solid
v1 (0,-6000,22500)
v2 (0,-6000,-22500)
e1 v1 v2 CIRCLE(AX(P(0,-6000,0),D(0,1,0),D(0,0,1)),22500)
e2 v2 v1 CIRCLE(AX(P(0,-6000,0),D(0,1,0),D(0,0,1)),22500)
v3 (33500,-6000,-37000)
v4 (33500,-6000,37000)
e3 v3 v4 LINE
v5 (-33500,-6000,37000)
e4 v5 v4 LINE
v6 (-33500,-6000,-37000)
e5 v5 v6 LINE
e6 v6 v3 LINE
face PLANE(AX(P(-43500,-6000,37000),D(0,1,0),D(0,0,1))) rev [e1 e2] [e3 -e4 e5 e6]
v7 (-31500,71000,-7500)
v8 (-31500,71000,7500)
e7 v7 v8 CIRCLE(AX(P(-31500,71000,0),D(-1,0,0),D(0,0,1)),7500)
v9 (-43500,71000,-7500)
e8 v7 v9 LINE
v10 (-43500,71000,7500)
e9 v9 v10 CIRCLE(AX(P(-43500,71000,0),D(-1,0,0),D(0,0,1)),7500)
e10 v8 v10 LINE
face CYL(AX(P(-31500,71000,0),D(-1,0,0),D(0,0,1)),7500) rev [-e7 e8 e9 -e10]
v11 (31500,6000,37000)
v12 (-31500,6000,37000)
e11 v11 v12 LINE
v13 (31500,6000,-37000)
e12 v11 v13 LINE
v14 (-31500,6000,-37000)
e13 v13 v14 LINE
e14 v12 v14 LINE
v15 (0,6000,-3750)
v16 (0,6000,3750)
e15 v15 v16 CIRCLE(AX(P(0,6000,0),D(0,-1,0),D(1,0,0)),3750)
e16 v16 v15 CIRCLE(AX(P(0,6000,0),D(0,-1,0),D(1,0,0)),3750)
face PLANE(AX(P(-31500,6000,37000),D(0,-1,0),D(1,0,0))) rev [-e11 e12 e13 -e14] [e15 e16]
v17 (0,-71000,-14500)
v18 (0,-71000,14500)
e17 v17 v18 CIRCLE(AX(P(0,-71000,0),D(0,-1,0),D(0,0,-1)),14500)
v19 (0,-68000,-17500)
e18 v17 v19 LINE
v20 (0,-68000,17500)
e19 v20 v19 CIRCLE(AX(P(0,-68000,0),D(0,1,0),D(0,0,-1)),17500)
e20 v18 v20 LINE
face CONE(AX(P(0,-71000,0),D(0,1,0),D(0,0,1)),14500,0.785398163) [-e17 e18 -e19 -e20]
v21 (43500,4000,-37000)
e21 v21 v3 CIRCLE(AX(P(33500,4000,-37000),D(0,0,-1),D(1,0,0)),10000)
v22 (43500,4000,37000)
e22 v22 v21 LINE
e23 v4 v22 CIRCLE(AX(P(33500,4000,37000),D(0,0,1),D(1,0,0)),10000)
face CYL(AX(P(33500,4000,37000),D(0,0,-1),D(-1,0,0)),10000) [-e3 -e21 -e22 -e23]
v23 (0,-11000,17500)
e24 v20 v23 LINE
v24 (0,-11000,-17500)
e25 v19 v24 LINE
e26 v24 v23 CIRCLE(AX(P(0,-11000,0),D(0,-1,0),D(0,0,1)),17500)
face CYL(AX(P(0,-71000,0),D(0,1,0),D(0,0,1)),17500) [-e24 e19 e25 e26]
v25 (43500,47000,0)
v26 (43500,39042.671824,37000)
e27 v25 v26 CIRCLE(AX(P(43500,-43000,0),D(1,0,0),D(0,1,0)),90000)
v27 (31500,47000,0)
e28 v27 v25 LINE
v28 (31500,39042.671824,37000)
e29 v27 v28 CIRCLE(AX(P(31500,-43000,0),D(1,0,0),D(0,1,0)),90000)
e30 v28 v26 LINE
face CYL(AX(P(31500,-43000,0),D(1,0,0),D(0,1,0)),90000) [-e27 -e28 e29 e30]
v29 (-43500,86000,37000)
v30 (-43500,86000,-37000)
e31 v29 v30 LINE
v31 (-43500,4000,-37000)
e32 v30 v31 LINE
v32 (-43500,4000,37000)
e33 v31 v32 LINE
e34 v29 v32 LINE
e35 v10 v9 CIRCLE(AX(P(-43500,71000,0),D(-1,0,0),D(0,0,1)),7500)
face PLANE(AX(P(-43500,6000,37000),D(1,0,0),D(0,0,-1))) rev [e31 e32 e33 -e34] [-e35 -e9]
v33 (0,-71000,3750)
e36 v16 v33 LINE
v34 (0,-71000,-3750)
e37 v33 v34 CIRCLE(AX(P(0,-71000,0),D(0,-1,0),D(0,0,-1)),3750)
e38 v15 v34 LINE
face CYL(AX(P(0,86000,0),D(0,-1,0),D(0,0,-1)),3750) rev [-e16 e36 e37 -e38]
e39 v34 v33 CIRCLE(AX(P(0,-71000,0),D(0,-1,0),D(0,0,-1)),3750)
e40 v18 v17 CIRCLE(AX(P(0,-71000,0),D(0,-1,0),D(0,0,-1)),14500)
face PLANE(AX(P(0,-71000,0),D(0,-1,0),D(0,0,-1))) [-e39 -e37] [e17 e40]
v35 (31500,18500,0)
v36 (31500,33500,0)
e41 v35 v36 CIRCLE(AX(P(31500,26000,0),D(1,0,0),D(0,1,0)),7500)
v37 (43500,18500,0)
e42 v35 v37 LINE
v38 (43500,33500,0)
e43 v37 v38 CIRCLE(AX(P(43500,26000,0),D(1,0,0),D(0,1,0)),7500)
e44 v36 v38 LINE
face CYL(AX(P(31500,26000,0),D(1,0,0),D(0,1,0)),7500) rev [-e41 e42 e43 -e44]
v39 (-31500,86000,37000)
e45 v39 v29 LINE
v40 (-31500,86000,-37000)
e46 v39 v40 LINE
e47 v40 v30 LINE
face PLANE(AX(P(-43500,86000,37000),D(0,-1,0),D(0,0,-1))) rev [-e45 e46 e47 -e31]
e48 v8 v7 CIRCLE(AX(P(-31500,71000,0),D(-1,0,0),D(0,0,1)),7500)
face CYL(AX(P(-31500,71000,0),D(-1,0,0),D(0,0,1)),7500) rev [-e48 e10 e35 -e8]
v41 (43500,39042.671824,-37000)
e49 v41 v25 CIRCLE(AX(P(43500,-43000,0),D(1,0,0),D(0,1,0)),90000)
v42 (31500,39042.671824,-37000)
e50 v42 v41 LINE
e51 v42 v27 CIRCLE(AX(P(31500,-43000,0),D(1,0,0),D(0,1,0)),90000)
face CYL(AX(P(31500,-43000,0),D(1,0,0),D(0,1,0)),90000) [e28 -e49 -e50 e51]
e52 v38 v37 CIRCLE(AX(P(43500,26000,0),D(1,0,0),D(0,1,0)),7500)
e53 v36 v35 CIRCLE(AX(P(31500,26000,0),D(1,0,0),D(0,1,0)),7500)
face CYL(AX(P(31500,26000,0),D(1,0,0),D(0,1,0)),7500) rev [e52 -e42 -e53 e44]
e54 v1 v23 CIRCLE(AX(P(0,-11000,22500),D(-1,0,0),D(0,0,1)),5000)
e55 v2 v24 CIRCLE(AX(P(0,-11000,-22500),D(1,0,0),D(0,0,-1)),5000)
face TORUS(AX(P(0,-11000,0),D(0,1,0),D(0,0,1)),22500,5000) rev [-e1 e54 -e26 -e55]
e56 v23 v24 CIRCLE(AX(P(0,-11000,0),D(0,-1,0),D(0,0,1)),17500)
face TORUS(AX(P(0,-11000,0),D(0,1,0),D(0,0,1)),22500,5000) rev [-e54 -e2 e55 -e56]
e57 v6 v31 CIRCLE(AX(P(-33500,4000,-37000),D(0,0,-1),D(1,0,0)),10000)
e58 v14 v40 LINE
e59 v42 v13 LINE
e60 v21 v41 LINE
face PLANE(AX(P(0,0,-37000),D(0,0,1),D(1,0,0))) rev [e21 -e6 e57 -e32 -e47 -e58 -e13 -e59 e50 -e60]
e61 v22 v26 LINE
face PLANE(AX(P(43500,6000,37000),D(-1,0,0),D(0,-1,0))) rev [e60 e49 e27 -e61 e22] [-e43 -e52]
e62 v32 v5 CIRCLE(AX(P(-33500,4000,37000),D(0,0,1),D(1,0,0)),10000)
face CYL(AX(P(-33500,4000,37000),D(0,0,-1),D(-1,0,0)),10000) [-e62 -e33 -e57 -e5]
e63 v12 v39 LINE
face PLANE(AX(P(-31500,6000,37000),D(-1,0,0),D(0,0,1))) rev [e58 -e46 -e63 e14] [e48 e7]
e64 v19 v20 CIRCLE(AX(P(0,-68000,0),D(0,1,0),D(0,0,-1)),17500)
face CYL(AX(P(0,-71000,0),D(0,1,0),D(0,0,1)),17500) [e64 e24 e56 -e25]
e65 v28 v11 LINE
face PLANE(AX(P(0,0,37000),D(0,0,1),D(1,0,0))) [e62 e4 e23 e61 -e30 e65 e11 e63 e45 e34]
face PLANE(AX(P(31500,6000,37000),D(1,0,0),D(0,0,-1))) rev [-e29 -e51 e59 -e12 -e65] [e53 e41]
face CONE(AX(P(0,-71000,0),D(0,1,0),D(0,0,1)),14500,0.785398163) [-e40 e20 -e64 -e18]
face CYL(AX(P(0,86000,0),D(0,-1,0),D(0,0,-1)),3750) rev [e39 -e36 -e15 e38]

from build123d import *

# Parameters (mm, degrees)
U_BRACKET_BODY_DEPTH                = 37000
CORNER_FILLET_R10_A_R               = 10000
CORNER_FILLET_R10_B_R               = 10000
SHORT_ARM_ARC_TOP_PROFILE_OUTSIDE_W = 103333.894
SHORT_ARM_ARC_TOP_PROFILE_OUTSIDE_H = 121333.894
SHORT_ARM_ARC_TOP_CUT_DEPTH         = 12000
SHORT_ARM_PIN_HOLE_SKETCH_R         = 7500
SHORT_ARM_PIN_HOLE_DEPTH            = 12000
TALL_ARM_PIN_HOLE_SKETCH_R          = 7500
TALL_ARM_PIN_HOLE_DEPTH             = 12000
SHANK_PROFILE_35_R                  = 17500
SHANK_35_DEPTH                      = 65000
SHANK_ROOT_FILLET_R5_R              = 5000
SHANK_END_CHAMFER_3X45_SIZE         = 3000
SHANK_HOLE_SKETCH_7_5_R             = 3750
SHANK_HOLE_7_5_DEPTH                = 167064.61063978


with BuildPart() as part:
    # U Bracket Profile → U Bracket Body (new, symmetric)
    with BuildSketch(Plane.XY):
        Polygon((-31500, 6000), (31500, 6000), (31500, 47000), (43500, 47000), (43500, 6000), (43500, -6000), (-43500, -6000), (-43500, 6000), (-43500, 86000), (-31500, 86000), align=None)
    extrude(amount=U_BRACKET_BODY_DEPTH, both=True)

    # Corner Fillet R10 A
    corner_fillet_r10_a_edges = [part.edges().sort_by_distance(p)[0] for p in [
        (43500, -6000, 0),
    ]]
    fillet(corner_fillet_r10_a_edges, radius=CORNER_FILLET_R10_A_R)

    # Corner Fillet R10 B
    corner_fillet_r10_b_edges = [part.edges().sort_by_distance(p)[0] for p in [
        (-43500, -6000, 0),
    ]]
    fillet(corner_fillet_r10_b_edges, radius=CORNER_FILLET_R10_B_R)

    # Short Arm Arc Top Profile outside → Short Arm Arc Top Cut (cut)
    with BuildSketch(Plane(origin=(43500, 0, 0), x_dir=(0, 0, -1), z_dir=(1, 0, 0))):
        with Locations((0, 40000)):
            Rectangle(SHORT_ARM_ARC_TOP_PROFILE_OUTSIDE_W, SHORT_ARM_ARC_TOP_PROFILE_OUTSIDE_H)
        with BuildLine():
            Line((-37000, 39042.671823875), (-37000, 4000))
            Line((-37000, 4000), (-37000, -6000))
            Line((-37000, -6000), (37000, -6000))
            Line((37000, -6000), (37000, 4000))
            Line((37000, 4000), (37000, 39042.671823875))
            ThreePointArc((37000, 39042.671823875), (0, 47000), (-37000, 39042.671823875))
        make_face(mode=Mode.SUBTRACT)
    extrude(amount=-SHORT_ARM_ARC_TOP_CUT_DEPTH, mode=Mode.SUBTRACT)

    # Short Arm Pin Hole Sketch → Short Arm Pin Hole (cut)
    with BuildSketch(Plane(origin=(43500, 0, 0), x_dir=(0, 0, -1), z_dir=(1, 0, 0))):
        with Locations(Location((0, 26000, 0), (0, 0, 90))):
            Circle(SHORT_ARM_PIN_HOLE_SKETCH_R)
    extrude(amount=-SHORT_ARM_PIN_HOLE_DEPTH, mode=Mode.SUBTRACT)

    # Tall Arm Pin Hole Sketch → Tall Arm Pin Hole (cut)
    with BuildSketch(Plane.ZY.offset(43500)):
        with Locations((0, 71000)):
            Circle(TALL_ARM_PIN_HOLE_SKETCH_R)
    extrude(amount=-TALL_ARM_PIN_HOLE_DEPTH, mode=Mode.SUBTRACT)

    # Shank Profile Ø35 → Shank Ø35 (add)
    with BuildSketch(Plane.XZ.offset(6000)):
        with Locations(Location((0, 0, 0), (0, 0, 90))):
            Circle(SHANK_PROFILE_35_R)
    extrude(amount=SHANK_35_DEPTH)

    # Shank Root Fillet R5
    shank_root_fillet_r5_edges = [part.edges().sort_by_distance(p)[0] for p in [
        (0, -6000, -17500),
    ]]
    fillet(shank_root_fillet_r5_edges, radius=SHANK_ROOT_FILLET_R5_R)

    # Shank End Chamfer 3x45
    shank_end_chamfer_3x45_edges = [part.edges().sort_by_distance(p)[0] for p in [
        (0, -71000, -17500),
    ]]
    chamfer(shank_end_chamfer_3x45_edges, length=SHANK_END_CHAMFER_3X45_SIZE)

    # Shank Hole Sketch Ø7.5 → Shank Hole Ø7.5 (cut, through all)
    with BuildSketch(Plane.XZ.offset(71000)):
        with Locations(Location((0, 0, 0), (0, 0, 270))):
            Circle(SHANK_HOLE_SKETCH_7_5_R)
    extrude(amount=-SHANK_HOLE_7_5_DEPTH, mode=Mode.SUBTRACT)


solid = part.part
